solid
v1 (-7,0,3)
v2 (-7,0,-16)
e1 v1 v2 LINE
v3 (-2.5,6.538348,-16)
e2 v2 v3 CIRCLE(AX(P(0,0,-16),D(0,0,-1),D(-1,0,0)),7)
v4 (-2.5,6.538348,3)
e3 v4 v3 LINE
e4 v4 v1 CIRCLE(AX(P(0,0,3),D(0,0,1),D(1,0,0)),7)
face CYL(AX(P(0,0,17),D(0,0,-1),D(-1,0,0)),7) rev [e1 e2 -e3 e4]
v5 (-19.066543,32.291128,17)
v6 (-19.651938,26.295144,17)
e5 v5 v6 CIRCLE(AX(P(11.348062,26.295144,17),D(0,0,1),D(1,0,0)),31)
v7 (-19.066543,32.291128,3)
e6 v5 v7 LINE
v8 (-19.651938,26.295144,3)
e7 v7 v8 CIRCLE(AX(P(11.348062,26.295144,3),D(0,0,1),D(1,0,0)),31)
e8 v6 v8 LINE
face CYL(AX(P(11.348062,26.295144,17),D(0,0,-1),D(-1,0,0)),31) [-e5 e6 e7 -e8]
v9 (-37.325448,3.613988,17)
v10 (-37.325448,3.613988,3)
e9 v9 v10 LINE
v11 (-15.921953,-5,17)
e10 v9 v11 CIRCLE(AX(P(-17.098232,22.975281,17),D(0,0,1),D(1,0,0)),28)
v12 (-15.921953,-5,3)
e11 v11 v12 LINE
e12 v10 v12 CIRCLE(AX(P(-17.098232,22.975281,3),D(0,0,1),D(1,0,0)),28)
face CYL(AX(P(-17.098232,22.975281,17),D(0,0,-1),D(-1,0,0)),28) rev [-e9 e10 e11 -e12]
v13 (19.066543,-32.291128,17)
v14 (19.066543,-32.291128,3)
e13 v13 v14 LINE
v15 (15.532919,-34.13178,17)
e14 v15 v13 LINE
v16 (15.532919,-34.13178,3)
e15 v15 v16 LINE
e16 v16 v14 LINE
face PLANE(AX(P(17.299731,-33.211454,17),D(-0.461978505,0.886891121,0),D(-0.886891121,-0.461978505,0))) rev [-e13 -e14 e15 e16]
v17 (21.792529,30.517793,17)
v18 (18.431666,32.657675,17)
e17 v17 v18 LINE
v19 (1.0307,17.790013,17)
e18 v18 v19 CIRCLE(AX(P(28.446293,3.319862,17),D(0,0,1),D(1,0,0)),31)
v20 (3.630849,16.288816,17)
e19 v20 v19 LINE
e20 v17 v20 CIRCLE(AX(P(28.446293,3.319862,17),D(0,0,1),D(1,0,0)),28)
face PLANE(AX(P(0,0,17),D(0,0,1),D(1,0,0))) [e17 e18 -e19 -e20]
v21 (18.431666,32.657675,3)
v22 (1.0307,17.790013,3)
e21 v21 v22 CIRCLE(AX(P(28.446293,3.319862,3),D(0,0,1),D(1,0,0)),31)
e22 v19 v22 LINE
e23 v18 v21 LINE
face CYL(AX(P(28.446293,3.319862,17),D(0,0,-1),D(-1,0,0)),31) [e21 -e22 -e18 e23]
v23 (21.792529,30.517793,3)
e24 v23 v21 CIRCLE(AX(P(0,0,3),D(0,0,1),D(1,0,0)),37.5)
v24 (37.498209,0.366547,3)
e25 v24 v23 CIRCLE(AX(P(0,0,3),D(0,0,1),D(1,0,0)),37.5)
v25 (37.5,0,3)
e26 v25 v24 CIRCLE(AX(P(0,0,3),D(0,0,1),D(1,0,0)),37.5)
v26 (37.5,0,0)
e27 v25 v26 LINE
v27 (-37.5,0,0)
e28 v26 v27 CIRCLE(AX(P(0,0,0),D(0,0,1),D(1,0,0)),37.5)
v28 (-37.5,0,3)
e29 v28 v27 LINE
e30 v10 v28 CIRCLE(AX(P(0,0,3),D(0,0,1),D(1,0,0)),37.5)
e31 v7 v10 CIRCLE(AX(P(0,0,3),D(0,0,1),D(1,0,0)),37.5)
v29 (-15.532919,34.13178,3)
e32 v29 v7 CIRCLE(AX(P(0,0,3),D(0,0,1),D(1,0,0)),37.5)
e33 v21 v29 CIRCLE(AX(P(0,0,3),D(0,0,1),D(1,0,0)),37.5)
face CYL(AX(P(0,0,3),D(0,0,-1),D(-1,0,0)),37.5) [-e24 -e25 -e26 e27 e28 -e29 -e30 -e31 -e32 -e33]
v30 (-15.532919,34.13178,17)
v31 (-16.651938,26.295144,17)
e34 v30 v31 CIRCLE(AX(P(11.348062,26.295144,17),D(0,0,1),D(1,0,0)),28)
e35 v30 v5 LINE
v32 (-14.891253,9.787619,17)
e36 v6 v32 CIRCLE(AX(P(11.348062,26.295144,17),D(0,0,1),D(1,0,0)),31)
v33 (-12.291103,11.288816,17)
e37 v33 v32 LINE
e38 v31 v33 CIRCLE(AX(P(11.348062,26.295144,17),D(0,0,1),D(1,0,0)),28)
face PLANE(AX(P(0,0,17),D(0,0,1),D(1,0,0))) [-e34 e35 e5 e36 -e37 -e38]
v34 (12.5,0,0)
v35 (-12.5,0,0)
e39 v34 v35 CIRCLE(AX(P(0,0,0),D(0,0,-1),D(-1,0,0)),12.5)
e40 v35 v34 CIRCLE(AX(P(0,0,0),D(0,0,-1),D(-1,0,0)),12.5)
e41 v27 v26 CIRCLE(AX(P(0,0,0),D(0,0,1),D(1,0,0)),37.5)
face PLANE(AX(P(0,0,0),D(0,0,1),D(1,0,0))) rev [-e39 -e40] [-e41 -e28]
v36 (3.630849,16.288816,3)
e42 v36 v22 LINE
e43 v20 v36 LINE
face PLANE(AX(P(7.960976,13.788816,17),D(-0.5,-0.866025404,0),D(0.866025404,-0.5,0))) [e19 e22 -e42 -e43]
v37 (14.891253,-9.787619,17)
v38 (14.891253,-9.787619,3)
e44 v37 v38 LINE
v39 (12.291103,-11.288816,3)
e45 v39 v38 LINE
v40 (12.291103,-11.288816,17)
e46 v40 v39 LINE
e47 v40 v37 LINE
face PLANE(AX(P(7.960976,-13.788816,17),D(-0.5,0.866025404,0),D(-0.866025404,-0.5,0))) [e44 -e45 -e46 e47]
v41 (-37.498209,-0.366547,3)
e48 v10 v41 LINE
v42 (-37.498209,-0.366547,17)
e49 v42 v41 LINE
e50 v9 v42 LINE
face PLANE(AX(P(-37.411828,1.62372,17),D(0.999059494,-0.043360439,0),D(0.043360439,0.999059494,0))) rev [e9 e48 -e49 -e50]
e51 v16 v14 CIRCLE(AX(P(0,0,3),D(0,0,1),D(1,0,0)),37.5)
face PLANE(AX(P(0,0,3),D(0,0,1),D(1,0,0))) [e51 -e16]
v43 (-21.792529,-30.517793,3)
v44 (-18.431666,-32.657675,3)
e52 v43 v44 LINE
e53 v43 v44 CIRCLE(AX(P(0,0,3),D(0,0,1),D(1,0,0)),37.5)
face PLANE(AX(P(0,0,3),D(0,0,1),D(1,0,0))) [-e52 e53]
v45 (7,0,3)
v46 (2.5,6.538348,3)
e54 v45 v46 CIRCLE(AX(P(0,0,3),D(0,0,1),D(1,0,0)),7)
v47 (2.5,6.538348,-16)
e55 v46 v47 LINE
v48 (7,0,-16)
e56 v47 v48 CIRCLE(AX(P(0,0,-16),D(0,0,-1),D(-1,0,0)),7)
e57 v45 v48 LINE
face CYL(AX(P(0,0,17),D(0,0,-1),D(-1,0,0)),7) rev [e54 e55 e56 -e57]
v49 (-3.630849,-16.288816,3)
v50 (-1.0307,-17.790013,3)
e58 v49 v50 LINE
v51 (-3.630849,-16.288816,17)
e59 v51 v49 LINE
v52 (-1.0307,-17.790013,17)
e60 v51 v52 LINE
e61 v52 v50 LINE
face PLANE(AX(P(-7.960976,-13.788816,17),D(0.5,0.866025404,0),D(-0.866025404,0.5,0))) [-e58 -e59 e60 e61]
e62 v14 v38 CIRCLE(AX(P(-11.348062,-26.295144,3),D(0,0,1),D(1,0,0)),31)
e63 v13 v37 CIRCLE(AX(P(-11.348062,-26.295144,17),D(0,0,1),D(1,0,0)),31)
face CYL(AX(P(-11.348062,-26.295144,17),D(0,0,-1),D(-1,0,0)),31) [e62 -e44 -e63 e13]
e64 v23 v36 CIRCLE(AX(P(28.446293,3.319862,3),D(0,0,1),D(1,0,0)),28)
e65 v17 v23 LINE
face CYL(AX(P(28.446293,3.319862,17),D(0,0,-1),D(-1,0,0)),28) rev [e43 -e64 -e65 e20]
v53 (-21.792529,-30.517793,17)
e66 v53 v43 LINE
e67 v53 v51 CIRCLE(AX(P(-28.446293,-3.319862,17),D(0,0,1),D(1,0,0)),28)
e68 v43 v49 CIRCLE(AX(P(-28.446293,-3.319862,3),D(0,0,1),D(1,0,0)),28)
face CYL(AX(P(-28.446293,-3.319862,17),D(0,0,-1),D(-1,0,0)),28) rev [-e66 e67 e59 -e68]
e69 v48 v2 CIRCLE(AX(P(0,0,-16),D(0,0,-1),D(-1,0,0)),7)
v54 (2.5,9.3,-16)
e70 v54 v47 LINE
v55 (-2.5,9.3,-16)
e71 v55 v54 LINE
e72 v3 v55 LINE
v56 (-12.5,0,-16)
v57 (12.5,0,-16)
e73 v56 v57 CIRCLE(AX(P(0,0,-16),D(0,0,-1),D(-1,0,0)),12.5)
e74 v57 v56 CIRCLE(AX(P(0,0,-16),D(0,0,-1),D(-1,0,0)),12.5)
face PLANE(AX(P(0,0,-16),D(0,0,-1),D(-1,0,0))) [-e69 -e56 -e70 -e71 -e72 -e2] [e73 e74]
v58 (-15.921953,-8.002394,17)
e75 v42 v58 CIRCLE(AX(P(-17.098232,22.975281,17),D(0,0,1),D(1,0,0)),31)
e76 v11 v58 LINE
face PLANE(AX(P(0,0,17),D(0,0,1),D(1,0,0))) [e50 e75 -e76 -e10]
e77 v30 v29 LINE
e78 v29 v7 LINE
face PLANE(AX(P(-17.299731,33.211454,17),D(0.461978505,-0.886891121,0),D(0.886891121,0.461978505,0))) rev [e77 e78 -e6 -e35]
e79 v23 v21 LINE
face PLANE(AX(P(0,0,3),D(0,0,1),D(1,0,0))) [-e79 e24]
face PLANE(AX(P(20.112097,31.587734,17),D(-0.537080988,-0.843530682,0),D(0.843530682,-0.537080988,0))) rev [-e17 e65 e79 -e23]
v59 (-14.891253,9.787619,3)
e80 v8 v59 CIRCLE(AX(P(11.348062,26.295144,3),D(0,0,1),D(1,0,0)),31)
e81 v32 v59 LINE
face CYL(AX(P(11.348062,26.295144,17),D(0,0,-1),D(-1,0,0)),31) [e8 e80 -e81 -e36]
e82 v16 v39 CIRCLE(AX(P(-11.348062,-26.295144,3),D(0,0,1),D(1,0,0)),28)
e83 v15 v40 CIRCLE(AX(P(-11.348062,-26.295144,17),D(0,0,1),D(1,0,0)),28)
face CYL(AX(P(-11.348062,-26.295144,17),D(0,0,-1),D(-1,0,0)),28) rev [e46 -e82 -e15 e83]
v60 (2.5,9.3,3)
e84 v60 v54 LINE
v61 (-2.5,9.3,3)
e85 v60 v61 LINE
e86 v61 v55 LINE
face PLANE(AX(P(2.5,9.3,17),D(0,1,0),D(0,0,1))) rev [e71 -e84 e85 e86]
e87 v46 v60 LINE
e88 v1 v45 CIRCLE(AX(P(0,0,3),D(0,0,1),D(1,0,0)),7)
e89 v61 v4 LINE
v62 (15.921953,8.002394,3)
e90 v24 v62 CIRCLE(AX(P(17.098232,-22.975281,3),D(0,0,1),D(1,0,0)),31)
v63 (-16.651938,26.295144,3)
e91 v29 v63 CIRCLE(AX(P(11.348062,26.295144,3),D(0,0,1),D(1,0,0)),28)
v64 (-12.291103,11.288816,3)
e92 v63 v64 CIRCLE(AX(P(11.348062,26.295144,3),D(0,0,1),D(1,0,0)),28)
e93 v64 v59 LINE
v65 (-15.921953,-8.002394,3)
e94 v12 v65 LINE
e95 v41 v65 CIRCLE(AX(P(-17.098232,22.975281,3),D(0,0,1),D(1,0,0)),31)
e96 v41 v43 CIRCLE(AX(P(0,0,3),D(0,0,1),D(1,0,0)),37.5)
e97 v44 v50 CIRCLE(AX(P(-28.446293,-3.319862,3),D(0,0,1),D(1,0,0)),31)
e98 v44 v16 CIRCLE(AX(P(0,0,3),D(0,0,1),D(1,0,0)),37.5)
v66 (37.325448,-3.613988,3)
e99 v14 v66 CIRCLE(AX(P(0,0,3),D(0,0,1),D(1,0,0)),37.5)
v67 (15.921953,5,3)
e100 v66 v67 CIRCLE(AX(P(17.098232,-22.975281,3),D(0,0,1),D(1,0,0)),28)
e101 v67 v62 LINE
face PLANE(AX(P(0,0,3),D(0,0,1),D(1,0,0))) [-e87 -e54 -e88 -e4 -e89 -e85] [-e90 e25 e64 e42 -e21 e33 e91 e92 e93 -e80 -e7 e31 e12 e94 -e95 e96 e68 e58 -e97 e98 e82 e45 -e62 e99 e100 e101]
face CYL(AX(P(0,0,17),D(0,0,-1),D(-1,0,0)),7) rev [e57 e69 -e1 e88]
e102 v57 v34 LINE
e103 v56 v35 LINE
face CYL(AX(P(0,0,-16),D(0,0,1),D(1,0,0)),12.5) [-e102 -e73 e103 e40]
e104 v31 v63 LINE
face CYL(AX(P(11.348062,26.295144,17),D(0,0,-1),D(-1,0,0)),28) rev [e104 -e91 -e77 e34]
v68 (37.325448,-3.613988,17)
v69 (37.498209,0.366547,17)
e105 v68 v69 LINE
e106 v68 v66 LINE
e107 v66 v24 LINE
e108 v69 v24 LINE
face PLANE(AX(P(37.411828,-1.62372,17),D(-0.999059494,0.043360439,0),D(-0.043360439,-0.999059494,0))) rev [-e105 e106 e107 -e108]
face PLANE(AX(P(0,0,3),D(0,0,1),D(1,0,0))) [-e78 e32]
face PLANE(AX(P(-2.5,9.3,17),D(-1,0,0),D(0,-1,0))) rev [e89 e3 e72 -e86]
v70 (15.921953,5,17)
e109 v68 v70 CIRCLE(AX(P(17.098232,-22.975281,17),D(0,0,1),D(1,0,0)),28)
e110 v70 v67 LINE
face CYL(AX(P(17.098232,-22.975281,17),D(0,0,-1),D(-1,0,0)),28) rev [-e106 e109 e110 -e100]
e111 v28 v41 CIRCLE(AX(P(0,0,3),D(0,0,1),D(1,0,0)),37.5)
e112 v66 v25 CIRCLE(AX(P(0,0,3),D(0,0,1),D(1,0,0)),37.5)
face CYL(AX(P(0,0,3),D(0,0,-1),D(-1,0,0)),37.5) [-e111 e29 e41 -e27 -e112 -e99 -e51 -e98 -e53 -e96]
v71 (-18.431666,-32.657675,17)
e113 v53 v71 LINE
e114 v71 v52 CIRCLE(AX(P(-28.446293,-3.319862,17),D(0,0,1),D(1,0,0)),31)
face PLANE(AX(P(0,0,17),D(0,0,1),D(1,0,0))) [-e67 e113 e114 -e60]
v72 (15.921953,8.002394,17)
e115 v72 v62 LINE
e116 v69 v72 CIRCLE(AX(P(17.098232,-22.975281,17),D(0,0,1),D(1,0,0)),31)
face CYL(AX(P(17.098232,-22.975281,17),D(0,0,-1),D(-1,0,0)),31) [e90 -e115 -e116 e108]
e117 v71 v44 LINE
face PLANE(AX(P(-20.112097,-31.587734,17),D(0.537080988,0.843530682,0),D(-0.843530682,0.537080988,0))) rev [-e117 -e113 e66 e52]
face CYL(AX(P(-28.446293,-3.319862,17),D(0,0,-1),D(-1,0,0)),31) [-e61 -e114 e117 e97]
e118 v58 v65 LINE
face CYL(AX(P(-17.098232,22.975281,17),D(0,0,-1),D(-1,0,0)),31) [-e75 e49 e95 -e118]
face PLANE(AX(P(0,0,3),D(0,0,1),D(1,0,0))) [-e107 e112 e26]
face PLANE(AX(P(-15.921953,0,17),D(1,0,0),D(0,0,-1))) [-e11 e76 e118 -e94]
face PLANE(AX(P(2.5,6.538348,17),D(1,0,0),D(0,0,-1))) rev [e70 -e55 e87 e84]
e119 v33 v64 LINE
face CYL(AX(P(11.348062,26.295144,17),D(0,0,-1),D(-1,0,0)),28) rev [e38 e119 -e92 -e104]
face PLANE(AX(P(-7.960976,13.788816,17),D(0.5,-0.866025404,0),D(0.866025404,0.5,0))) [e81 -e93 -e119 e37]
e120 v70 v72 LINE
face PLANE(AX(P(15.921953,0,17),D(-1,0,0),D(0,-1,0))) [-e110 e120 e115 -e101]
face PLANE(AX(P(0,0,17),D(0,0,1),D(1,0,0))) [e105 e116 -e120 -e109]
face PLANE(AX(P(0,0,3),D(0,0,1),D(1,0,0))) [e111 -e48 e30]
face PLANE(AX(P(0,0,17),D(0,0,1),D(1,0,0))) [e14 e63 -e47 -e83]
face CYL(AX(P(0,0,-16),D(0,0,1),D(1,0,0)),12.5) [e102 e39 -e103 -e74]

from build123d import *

# Parameters (mm, degrees)
BACK_DISC_SKETCH_R        = 37.5
BACK_DISC_75_DEPTH        = 3
BLADES_6X_DEPTH           = 14
HUB_SKETCH_R              = 12.5
HUB_25_DEPTH              = 16
KEYED_SHAFT_BORE_14_DEPTH = 63.461988441


with BuildPart() as part:
    # Back Disc Sketch → Back Disc Ø75 (new body)
    with BuildSketch(Plane.XY):
        Circle(BACK_DISC_SKETCH_R)
    extrude(amount=BACK_DISC_75_DEPTH)

    # Blade Profiles Sketch → Blades 6x (add)
    with BuildSketch(Plane.XY.offset(3)):
        with BuildLine():
            ThreePointArc((3.63084944, 16.288815705), (11.178007051, 25.36087614), (21.79252918, 30.51779271))
            Line((21.79252918, 30.51779271), (18.431665522, 32.657674536))
            ThreePointArc((18.431665522, 32.657674536), (8.308835539, 26.888544841), (1.030700016, 17.790012675))
            Line((1.030700016, 17.790012675), (3.63084944, 16.288815705))
        make_face()
        with BuildLine():
            ThreePointArc((-12.291103478, 11.288815705), (-16.374159474, 22.36087614), (-15.532919164, 34.131780238))
            Line((-15.532919164, 34.131780238), (-19.066543016, 32.291127844))
            ThreePointArc((-19.066543016, 32.291127844), (-19.131745134, 20.639935074), (-14.891252903, 9.787618735))
            Line((-14.891252903, 9.787618735), (-12.291103478, 11.288815705))
        make_face()
        with BuildLine():
            ThreePointArc((-15.921952918, -5), (-27.552166525, -3), (-37.325448345, 3.613987528))
            Line((-37.325448345, 3.613987528), (-37.498208538, -0.366546692))
            ThreePointArc((-37.498208538, -0.366546692), (-27.440580673, -6.248609768), (-15.921952918, -8.00239394))
            Line((-15.921952918, -8.00239394), (-15.921952918, -5))
        make_face()
        with BuildLine():
            ThreePointArc((-3.63084944, -16.288815705), (-11.178007051, -25.36087614), (-21.79252918, -30.51779271))
            Line((-21.79252918, -30.51779271), (-18.431665522, -32.657674536))
            ThreePointArc((-18.431665522, -32.657674536), (-8.308835539, -26.888544841), (-1.030700016, -17.790012675))
            Line((-1.030700016, -17.790012675), (-3.63084944, -16.288815705))
        make_face()
        with BuildLine():
            ThreePointArc((12.291103478, -11.288815705), (16.374159474, -22.36087614), (15.532919164, -34.131780238))
            Line((15.532919164, -34.131780238), (19.066543016, -32.291127844))
            ThreePointArc((19.066543016, -32.291127844), (19.131745134, -20.639935074), (14.891252903, -9.787618735))
            Line((14.891252903, -9.787618735), (12.291103478, -11.288815705))
        make_face()
        with BuildLine():
            ThreePointArc((15.921952918, 5), (27.552166525, 3), (37.325448345, -3.613987528))
            Line((37.325448345, -3.613987528), (37.498208538, 0.366546692))
            ThreePointArc((37.498208538, 0.366546692), (27.440580673, 6.248609768), (15.921952918, 8.00239394))
            Line((15.921952918, 8.00239394), (15.921952918, 5))
        make_face()
    extrude(amount=BLADES_6X_DEPTH)

    # Hub Sketch → Hub Ø25 (add)
    with BuildSketch(Plane(origin=(0, 0, 0), x_dir=(-1, 0, 0), z_dir=(0, 0, -1))):
        Circle(HUB_SKETCH_R)
    extrude(amount=HUB_25_DEPTH)

    # Shaft Bore Sketch → Keyed Shaft Bore Ø14 (cut, through all)
    with BuildSketch(Plane(origin=(0, 0, -16), x_dir=(-1, 0, 0), z_dir=(0, 0, -1))):
        with BuildLine():
            Line((-2.5, 6.538348415), (-2.5, 9.3))
            Line((-2.5, 9.3), (2.5, 9.3))
            Line((2.5, 9.3), (2.5, 6.538348415))
            ThreePointArc((2.5, 6.538348415), (0, -7), (-2.5, 6.538348415))
        make_face()
    extrude(amount=-KEYED_SHAFT_BORE_14_DEPTH, mode=Mode.SUBTRACT)


solid = part.part
